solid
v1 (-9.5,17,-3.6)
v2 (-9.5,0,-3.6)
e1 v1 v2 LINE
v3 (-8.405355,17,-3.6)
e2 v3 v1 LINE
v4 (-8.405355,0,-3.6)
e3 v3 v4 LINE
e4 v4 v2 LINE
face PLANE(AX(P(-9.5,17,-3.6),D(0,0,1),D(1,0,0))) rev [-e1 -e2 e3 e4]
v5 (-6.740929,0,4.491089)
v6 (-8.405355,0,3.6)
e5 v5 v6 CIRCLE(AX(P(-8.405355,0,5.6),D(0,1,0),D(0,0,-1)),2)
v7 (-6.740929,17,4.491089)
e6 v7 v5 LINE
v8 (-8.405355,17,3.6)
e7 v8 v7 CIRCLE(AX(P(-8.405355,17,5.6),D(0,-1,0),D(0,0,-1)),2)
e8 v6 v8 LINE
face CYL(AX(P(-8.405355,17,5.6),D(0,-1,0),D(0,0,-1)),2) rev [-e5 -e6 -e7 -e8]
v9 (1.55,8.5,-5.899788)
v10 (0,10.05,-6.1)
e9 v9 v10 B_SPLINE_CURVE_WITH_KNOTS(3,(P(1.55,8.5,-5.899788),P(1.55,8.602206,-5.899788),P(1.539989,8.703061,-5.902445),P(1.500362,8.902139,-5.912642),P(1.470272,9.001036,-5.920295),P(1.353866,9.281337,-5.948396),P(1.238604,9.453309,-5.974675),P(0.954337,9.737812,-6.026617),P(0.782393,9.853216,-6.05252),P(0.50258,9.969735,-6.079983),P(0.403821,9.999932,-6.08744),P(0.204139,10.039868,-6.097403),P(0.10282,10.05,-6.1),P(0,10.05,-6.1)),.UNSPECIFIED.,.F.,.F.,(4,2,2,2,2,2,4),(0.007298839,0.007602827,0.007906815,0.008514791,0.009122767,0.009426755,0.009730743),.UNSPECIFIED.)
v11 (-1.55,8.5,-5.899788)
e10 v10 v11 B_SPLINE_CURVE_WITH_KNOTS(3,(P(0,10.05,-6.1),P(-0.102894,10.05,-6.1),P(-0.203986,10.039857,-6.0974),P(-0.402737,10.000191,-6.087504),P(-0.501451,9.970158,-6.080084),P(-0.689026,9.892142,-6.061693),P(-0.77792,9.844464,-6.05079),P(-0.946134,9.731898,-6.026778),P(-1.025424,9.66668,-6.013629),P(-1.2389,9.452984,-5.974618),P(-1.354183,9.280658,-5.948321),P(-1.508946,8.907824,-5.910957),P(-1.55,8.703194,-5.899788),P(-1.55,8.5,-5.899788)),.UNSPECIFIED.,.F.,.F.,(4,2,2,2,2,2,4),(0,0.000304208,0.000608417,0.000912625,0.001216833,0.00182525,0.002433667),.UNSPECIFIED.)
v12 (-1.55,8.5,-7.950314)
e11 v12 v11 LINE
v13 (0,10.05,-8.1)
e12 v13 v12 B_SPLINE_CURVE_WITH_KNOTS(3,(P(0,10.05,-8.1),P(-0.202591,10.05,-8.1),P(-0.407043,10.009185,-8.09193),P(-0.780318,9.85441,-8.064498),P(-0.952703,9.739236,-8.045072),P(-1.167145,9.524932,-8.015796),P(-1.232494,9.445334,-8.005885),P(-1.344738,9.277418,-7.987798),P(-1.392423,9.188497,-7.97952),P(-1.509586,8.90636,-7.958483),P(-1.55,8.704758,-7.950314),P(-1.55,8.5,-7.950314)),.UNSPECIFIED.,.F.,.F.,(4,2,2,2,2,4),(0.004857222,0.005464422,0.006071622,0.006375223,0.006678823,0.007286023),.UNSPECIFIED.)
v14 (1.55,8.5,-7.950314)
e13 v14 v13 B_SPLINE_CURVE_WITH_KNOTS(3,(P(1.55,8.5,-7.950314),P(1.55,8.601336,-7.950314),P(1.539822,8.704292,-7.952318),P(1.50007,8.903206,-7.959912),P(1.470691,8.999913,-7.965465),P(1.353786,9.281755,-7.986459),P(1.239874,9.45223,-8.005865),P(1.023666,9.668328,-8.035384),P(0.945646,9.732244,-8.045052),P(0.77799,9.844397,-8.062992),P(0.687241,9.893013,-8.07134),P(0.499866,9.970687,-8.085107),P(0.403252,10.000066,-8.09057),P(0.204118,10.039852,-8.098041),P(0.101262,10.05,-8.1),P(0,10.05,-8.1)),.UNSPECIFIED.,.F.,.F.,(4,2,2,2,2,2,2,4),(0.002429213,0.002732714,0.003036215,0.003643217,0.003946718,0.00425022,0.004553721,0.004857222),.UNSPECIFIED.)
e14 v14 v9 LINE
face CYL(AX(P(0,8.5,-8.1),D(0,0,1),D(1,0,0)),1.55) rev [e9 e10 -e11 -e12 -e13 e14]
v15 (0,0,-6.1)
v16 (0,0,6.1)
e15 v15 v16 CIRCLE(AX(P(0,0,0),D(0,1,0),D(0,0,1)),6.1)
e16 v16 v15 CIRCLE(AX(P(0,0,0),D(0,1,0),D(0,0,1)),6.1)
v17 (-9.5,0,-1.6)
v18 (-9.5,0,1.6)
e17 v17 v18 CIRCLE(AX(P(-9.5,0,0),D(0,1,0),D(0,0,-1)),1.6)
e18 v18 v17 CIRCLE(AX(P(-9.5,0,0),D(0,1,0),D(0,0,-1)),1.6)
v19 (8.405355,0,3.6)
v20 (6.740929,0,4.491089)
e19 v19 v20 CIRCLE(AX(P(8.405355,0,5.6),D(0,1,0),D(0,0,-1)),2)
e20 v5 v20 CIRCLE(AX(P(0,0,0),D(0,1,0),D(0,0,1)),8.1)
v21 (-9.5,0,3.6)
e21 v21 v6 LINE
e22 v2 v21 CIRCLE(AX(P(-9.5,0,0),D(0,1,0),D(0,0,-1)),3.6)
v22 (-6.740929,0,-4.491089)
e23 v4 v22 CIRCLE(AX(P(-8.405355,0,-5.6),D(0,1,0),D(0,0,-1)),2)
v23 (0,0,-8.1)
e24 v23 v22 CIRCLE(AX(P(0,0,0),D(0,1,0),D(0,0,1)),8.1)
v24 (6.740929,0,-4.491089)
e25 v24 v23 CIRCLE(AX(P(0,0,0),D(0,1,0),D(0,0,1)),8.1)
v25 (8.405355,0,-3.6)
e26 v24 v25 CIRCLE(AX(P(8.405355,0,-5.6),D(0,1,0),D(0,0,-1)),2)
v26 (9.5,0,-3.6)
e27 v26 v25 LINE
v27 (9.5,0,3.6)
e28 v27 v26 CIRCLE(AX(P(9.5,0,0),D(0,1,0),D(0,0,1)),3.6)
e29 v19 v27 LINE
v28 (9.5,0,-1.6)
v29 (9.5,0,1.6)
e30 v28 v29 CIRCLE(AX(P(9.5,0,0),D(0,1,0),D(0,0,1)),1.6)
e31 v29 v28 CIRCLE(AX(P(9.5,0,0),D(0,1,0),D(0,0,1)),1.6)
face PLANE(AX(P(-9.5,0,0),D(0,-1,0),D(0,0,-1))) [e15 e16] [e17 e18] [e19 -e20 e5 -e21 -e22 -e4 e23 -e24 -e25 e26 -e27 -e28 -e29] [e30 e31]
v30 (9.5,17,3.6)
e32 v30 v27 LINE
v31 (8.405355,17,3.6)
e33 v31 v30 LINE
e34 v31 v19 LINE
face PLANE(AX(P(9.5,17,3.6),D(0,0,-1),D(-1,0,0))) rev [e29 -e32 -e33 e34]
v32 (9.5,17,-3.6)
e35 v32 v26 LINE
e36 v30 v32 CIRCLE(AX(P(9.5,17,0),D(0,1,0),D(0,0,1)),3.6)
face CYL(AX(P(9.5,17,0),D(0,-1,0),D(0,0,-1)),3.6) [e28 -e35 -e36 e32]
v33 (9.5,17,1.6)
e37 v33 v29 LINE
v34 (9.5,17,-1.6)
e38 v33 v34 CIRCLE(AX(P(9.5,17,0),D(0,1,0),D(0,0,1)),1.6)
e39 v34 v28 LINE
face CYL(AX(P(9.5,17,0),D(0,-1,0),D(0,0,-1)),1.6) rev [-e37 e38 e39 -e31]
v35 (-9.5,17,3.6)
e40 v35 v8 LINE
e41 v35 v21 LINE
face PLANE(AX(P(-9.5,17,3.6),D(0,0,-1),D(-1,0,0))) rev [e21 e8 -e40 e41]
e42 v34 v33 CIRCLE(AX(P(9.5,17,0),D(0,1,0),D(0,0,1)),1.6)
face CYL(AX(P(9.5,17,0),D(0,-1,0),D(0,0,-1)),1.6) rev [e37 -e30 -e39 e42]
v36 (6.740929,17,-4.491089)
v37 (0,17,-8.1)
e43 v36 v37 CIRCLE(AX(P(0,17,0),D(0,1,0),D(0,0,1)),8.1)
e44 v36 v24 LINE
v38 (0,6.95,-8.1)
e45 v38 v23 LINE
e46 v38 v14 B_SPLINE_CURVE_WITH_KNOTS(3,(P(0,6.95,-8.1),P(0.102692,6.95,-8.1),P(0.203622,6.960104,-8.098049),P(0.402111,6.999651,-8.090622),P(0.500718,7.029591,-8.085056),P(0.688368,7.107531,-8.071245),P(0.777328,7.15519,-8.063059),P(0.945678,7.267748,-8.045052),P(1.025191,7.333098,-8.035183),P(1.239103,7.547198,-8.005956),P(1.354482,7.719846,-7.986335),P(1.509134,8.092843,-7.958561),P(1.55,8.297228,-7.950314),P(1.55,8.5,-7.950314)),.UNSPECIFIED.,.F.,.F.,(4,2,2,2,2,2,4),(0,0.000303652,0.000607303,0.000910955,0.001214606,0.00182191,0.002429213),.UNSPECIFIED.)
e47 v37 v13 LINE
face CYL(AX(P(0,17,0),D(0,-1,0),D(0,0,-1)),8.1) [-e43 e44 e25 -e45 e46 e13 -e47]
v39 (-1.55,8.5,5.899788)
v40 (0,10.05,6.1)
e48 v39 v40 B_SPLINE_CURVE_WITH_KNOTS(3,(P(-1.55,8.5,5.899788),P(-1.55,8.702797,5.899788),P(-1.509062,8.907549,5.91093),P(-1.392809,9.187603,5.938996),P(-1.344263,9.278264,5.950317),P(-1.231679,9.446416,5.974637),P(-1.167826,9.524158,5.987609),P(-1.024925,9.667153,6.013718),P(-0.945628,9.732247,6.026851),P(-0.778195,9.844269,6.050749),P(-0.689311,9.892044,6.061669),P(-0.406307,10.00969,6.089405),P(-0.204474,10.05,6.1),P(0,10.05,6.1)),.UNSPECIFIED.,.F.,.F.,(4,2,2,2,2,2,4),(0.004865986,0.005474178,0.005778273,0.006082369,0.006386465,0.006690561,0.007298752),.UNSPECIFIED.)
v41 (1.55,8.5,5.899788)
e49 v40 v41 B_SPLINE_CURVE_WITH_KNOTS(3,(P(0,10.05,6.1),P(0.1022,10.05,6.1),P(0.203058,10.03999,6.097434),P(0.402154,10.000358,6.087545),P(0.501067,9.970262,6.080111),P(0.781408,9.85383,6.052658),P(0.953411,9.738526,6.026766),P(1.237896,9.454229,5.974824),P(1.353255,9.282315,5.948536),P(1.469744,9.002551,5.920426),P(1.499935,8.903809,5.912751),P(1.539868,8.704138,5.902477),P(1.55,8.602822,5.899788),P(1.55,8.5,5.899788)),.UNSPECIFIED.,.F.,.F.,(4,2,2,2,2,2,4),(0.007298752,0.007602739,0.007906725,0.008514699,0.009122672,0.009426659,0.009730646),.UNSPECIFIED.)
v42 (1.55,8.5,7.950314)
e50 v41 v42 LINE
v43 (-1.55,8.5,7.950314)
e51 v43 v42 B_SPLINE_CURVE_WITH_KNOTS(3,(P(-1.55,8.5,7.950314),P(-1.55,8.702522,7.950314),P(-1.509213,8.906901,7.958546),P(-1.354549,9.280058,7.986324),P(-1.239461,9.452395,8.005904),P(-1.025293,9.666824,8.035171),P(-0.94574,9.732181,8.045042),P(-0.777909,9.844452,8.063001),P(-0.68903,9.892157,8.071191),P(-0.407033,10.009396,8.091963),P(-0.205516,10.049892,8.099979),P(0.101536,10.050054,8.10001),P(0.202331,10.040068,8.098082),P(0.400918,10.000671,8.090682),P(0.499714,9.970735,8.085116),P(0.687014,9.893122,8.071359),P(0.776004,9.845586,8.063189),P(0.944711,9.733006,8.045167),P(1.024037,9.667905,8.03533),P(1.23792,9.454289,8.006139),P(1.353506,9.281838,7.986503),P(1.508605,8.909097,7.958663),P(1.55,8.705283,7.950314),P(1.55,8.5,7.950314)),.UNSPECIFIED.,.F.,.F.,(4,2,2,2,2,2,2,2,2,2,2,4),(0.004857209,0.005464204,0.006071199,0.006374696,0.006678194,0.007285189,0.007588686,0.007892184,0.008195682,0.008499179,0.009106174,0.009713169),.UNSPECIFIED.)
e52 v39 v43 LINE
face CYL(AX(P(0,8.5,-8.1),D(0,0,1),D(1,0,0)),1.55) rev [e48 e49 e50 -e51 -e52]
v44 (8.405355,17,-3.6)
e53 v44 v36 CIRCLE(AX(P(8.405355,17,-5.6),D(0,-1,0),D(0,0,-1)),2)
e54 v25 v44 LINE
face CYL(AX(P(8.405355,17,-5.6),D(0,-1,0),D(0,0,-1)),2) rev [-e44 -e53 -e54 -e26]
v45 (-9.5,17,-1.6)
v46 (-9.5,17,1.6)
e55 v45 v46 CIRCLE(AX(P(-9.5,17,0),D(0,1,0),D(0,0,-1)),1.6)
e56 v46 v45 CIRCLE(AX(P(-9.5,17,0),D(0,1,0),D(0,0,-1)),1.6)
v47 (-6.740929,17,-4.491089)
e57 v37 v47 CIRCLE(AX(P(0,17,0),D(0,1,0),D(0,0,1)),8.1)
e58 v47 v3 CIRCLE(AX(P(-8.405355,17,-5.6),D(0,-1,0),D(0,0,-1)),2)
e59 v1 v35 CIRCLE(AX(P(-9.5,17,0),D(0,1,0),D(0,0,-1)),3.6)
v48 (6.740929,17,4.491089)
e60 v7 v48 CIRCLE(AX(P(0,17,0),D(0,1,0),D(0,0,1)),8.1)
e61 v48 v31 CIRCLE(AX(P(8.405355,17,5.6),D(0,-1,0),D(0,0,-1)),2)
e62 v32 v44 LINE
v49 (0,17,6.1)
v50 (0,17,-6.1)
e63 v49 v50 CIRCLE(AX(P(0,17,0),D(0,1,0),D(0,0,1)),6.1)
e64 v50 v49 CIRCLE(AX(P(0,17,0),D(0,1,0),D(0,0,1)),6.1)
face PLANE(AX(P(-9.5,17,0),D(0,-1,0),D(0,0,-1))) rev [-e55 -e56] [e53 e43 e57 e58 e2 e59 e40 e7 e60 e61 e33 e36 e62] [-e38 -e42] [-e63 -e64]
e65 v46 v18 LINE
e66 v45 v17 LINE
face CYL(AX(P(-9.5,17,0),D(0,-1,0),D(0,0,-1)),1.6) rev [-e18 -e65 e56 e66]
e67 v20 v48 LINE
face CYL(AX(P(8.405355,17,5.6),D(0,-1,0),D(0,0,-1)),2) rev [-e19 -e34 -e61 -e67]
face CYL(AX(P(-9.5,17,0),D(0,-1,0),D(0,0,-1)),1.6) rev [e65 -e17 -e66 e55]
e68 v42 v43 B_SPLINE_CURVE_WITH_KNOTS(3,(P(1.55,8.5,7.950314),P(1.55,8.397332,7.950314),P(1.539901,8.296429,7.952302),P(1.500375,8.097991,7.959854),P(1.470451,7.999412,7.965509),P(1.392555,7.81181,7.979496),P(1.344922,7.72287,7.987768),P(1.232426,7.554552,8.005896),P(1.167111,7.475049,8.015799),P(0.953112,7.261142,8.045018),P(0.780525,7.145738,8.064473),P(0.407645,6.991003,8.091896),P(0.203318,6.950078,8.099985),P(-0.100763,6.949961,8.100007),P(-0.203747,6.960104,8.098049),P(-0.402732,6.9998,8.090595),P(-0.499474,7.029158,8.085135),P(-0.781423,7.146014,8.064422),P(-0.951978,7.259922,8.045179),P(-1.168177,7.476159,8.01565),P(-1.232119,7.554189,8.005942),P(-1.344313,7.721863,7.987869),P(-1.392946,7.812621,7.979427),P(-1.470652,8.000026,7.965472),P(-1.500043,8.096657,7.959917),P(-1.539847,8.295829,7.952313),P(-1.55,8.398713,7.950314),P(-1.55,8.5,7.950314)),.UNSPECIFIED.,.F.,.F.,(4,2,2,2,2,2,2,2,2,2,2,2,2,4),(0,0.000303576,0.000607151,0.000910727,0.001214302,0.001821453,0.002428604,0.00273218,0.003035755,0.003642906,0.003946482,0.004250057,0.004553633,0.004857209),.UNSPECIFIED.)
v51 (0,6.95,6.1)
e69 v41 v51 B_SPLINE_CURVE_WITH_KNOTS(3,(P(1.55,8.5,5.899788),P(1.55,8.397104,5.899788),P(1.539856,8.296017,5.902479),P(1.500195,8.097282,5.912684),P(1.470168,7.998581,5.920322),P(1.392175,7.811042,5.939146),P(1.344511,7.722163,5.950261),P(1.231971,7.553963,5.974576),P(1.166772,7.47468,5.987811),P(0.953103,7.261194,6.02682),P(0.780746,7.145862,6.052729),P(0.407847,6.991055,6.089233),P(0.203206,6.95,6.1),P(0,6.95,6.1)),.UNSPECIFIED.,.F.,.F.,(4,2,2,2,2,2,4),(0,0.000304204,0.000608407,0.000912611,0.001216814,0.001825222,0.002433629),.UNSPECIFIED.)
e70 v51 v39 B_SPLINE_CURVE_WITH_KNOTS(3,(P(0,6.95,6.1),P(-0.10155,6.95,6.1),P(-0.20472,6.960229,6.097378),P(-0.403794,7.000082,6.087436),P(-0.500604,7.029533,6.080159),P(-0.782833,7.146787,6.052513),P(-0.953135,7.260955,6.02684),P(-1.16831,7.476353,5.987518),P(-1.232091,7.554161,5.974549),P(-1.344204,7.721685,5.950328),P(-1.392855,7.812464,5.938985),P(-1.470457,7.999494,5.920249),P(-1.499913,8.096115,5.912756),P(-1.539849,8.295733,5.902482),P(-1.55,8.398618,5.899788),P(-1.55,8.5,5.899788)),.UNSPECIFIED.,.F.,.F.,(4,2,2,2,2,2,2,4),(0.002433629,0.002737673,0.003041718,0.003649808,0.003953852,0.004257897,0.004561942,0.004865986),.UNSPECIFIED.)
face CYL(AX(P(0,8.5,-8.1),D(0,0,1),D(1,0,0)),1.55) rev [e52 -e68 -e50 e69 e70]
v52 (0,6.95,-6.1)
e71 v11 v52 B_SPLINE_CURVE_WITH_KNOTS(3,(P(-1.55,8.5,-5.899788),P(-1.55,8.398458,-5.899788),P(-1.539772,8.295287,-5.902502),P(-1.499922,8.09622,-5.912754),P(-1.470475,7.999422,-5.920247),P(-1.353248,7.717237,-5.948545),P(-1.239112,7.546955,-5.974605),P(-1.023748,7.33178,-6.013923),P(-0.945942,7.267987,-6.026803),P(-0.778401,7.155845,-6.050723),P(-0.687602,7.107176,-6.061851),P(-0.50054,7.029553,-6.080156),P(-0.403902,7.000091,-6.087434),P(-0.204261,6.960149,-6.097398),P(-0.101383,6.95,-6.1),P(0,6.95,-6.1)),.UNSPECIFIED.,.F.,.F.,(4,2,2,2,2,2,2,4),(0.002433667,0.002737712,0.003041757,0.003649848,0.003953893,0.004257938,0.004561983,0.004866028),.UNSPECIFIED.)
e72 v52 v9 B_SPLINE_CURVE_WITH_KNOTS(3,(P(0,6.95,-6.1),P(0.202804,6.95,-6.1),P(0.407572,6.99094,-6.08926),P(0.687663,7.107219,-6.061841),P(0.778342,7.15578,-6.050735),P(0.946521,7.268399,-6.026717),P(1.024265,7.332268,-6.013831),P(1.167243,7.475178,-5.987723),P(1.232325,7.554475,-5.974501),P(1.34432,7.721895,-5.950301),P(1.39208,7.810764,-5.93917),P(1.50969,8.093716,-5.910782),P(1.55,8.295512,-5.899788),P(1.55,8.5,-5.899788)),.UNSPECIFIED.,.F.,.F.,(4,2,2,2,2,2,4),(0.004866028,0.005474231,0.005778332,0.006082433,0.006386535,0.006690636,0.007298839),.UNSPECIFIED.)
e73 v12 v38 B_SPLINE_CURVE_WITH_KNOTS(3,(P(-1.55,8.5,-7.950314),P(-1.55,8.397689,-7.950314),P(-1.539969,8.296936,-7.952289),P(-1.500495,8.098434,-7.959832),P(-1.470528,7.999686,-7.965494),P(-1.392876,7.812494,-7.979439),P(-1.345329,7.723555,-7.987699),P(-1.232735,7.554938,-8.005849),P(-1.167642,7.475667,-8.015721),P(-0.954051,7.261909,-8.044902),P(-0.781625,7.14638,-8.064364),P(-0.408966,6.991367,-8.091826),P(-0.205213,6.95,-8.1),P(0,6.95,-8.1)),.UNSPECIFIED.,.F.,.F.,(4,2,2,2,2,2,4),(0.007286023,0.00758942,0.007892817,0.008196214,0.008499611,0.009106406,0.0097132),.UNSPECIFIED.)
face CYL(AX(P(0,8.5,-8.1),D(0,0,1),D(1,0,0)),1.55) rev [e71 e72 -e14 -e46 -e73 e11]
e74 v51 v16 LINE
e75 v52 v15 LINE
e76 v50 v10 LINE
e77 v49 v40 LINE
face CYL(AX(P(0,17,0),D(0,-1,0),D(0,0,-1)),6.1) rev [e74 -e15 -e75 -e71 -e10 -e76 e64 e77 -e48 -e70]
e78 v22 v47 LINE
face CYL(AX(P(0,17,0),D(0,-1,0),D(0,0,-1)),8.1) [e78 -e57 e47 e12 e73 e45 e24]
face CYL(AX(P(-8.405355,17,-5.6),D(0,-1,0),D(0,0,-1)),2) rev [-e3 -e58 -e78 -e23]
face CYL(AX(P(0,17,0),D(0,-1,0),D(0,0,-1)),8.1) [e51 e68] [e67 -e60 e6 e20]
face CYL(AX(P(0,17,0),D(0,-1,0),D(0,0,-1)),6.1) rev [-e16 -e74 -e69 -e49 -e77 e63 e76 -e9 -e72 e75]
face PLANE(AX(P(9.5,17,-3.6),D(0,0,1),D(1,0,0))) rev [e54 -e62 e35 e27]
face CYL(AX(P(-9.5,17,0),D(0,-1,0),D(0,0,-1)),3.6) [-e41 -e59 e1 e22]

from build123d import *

# Parameters (mm, degrees)
SKETCH_1_R               = 6.1
SKETCH_1_R_2             = 1.6
EXTRUDE_1_DEPTH          = 17
FILLET_1_R               = 2
CUT_EXTRUDE_1_DEPTH      = 23.939485609
CUT_EXTRUDE_1_DEPTH_BACK = 23.939485609
SKETCH_2_R               = 1.55


with BuildPart() as part:
    # 草图1 → 凸台-拉伸1 (new body)
    with BuildSketch(Plane(origin=(0, 0, 0), x_dir=(1, 0, 0), z_dir=(0, 1, 0))):
        with BuildLine():
            Line((9.5, 3.6), (7.256031973, 3.6))
            ThreePointArc((7.256031973, 3.6), (0, 8.1), (-7.256031973, 3.6))
            Line((-7.256031973, 3.6), (-9.5, 3.6))
            ThreePointArc((-9.5, 3.6), (-13.1, 0), (-9.5, -3.6))
            Line((-9.5, -3.6), (-7.256031973, -3.6))
            ThreePointArc((-7.256031973, -3.6), (0, -8.1), (7.256031973, -3.6))
            Line((7.256031973, -3.6), (9.5, -3.6))
            ThreePointArc((9.5, -3.6), (13.1, 0), (9.5, 3.6))
        make_face()
        with Locations(Location((0, 0, 0), (0, 0, 270))):
            Circle(SKETCH_1_R, mode=Mode.SUBTRACT)
        with Locations(Location((9.5, 0, 0), (0, 0, 270))):
            Circle(SKETCH_1_R_2, mode=Mode.SUBTRACT)
        with Locations(Location((-9.5, 0, 0), (0, 0, 90))):
            Circle(SKETCH_1_R_2, mode=Mode.SUBTRACT)
    extrude(amount=EXTRUDE_1_DEPTH)

    # 圆角1
    fillet_1_edges = [part.edges().sort_by_distance(p)[0] for p in [
        (-7.256031973, 8.5, -3.6),
        (7.256031973, 8.5, -3.6),
        (7.256031973, 8.5, 3.6),
        (-7.256031973, 8.5, 3.6),
    ]]
    fillet(fillet_1_edges, radius=FILLET_1_R)

    # 草图2 → 切除-拉伸1 (cut, two sides: drawn at the far end of the back side and taken through both)
    with BuildSketch(Plane.XY.offset(-CUT_EXTRUDE_1_DEPTH_BACK)):
        with Locations((0, 8.5)):
            Circle(SKETCH_2_R)
    extrude(amount=CUT_EXTRUDE_1_DEPTH + CUT_EXTRUDE_1_DEPTH_BACK, mode=Mode.SUBTRACT)


solid = part.part
